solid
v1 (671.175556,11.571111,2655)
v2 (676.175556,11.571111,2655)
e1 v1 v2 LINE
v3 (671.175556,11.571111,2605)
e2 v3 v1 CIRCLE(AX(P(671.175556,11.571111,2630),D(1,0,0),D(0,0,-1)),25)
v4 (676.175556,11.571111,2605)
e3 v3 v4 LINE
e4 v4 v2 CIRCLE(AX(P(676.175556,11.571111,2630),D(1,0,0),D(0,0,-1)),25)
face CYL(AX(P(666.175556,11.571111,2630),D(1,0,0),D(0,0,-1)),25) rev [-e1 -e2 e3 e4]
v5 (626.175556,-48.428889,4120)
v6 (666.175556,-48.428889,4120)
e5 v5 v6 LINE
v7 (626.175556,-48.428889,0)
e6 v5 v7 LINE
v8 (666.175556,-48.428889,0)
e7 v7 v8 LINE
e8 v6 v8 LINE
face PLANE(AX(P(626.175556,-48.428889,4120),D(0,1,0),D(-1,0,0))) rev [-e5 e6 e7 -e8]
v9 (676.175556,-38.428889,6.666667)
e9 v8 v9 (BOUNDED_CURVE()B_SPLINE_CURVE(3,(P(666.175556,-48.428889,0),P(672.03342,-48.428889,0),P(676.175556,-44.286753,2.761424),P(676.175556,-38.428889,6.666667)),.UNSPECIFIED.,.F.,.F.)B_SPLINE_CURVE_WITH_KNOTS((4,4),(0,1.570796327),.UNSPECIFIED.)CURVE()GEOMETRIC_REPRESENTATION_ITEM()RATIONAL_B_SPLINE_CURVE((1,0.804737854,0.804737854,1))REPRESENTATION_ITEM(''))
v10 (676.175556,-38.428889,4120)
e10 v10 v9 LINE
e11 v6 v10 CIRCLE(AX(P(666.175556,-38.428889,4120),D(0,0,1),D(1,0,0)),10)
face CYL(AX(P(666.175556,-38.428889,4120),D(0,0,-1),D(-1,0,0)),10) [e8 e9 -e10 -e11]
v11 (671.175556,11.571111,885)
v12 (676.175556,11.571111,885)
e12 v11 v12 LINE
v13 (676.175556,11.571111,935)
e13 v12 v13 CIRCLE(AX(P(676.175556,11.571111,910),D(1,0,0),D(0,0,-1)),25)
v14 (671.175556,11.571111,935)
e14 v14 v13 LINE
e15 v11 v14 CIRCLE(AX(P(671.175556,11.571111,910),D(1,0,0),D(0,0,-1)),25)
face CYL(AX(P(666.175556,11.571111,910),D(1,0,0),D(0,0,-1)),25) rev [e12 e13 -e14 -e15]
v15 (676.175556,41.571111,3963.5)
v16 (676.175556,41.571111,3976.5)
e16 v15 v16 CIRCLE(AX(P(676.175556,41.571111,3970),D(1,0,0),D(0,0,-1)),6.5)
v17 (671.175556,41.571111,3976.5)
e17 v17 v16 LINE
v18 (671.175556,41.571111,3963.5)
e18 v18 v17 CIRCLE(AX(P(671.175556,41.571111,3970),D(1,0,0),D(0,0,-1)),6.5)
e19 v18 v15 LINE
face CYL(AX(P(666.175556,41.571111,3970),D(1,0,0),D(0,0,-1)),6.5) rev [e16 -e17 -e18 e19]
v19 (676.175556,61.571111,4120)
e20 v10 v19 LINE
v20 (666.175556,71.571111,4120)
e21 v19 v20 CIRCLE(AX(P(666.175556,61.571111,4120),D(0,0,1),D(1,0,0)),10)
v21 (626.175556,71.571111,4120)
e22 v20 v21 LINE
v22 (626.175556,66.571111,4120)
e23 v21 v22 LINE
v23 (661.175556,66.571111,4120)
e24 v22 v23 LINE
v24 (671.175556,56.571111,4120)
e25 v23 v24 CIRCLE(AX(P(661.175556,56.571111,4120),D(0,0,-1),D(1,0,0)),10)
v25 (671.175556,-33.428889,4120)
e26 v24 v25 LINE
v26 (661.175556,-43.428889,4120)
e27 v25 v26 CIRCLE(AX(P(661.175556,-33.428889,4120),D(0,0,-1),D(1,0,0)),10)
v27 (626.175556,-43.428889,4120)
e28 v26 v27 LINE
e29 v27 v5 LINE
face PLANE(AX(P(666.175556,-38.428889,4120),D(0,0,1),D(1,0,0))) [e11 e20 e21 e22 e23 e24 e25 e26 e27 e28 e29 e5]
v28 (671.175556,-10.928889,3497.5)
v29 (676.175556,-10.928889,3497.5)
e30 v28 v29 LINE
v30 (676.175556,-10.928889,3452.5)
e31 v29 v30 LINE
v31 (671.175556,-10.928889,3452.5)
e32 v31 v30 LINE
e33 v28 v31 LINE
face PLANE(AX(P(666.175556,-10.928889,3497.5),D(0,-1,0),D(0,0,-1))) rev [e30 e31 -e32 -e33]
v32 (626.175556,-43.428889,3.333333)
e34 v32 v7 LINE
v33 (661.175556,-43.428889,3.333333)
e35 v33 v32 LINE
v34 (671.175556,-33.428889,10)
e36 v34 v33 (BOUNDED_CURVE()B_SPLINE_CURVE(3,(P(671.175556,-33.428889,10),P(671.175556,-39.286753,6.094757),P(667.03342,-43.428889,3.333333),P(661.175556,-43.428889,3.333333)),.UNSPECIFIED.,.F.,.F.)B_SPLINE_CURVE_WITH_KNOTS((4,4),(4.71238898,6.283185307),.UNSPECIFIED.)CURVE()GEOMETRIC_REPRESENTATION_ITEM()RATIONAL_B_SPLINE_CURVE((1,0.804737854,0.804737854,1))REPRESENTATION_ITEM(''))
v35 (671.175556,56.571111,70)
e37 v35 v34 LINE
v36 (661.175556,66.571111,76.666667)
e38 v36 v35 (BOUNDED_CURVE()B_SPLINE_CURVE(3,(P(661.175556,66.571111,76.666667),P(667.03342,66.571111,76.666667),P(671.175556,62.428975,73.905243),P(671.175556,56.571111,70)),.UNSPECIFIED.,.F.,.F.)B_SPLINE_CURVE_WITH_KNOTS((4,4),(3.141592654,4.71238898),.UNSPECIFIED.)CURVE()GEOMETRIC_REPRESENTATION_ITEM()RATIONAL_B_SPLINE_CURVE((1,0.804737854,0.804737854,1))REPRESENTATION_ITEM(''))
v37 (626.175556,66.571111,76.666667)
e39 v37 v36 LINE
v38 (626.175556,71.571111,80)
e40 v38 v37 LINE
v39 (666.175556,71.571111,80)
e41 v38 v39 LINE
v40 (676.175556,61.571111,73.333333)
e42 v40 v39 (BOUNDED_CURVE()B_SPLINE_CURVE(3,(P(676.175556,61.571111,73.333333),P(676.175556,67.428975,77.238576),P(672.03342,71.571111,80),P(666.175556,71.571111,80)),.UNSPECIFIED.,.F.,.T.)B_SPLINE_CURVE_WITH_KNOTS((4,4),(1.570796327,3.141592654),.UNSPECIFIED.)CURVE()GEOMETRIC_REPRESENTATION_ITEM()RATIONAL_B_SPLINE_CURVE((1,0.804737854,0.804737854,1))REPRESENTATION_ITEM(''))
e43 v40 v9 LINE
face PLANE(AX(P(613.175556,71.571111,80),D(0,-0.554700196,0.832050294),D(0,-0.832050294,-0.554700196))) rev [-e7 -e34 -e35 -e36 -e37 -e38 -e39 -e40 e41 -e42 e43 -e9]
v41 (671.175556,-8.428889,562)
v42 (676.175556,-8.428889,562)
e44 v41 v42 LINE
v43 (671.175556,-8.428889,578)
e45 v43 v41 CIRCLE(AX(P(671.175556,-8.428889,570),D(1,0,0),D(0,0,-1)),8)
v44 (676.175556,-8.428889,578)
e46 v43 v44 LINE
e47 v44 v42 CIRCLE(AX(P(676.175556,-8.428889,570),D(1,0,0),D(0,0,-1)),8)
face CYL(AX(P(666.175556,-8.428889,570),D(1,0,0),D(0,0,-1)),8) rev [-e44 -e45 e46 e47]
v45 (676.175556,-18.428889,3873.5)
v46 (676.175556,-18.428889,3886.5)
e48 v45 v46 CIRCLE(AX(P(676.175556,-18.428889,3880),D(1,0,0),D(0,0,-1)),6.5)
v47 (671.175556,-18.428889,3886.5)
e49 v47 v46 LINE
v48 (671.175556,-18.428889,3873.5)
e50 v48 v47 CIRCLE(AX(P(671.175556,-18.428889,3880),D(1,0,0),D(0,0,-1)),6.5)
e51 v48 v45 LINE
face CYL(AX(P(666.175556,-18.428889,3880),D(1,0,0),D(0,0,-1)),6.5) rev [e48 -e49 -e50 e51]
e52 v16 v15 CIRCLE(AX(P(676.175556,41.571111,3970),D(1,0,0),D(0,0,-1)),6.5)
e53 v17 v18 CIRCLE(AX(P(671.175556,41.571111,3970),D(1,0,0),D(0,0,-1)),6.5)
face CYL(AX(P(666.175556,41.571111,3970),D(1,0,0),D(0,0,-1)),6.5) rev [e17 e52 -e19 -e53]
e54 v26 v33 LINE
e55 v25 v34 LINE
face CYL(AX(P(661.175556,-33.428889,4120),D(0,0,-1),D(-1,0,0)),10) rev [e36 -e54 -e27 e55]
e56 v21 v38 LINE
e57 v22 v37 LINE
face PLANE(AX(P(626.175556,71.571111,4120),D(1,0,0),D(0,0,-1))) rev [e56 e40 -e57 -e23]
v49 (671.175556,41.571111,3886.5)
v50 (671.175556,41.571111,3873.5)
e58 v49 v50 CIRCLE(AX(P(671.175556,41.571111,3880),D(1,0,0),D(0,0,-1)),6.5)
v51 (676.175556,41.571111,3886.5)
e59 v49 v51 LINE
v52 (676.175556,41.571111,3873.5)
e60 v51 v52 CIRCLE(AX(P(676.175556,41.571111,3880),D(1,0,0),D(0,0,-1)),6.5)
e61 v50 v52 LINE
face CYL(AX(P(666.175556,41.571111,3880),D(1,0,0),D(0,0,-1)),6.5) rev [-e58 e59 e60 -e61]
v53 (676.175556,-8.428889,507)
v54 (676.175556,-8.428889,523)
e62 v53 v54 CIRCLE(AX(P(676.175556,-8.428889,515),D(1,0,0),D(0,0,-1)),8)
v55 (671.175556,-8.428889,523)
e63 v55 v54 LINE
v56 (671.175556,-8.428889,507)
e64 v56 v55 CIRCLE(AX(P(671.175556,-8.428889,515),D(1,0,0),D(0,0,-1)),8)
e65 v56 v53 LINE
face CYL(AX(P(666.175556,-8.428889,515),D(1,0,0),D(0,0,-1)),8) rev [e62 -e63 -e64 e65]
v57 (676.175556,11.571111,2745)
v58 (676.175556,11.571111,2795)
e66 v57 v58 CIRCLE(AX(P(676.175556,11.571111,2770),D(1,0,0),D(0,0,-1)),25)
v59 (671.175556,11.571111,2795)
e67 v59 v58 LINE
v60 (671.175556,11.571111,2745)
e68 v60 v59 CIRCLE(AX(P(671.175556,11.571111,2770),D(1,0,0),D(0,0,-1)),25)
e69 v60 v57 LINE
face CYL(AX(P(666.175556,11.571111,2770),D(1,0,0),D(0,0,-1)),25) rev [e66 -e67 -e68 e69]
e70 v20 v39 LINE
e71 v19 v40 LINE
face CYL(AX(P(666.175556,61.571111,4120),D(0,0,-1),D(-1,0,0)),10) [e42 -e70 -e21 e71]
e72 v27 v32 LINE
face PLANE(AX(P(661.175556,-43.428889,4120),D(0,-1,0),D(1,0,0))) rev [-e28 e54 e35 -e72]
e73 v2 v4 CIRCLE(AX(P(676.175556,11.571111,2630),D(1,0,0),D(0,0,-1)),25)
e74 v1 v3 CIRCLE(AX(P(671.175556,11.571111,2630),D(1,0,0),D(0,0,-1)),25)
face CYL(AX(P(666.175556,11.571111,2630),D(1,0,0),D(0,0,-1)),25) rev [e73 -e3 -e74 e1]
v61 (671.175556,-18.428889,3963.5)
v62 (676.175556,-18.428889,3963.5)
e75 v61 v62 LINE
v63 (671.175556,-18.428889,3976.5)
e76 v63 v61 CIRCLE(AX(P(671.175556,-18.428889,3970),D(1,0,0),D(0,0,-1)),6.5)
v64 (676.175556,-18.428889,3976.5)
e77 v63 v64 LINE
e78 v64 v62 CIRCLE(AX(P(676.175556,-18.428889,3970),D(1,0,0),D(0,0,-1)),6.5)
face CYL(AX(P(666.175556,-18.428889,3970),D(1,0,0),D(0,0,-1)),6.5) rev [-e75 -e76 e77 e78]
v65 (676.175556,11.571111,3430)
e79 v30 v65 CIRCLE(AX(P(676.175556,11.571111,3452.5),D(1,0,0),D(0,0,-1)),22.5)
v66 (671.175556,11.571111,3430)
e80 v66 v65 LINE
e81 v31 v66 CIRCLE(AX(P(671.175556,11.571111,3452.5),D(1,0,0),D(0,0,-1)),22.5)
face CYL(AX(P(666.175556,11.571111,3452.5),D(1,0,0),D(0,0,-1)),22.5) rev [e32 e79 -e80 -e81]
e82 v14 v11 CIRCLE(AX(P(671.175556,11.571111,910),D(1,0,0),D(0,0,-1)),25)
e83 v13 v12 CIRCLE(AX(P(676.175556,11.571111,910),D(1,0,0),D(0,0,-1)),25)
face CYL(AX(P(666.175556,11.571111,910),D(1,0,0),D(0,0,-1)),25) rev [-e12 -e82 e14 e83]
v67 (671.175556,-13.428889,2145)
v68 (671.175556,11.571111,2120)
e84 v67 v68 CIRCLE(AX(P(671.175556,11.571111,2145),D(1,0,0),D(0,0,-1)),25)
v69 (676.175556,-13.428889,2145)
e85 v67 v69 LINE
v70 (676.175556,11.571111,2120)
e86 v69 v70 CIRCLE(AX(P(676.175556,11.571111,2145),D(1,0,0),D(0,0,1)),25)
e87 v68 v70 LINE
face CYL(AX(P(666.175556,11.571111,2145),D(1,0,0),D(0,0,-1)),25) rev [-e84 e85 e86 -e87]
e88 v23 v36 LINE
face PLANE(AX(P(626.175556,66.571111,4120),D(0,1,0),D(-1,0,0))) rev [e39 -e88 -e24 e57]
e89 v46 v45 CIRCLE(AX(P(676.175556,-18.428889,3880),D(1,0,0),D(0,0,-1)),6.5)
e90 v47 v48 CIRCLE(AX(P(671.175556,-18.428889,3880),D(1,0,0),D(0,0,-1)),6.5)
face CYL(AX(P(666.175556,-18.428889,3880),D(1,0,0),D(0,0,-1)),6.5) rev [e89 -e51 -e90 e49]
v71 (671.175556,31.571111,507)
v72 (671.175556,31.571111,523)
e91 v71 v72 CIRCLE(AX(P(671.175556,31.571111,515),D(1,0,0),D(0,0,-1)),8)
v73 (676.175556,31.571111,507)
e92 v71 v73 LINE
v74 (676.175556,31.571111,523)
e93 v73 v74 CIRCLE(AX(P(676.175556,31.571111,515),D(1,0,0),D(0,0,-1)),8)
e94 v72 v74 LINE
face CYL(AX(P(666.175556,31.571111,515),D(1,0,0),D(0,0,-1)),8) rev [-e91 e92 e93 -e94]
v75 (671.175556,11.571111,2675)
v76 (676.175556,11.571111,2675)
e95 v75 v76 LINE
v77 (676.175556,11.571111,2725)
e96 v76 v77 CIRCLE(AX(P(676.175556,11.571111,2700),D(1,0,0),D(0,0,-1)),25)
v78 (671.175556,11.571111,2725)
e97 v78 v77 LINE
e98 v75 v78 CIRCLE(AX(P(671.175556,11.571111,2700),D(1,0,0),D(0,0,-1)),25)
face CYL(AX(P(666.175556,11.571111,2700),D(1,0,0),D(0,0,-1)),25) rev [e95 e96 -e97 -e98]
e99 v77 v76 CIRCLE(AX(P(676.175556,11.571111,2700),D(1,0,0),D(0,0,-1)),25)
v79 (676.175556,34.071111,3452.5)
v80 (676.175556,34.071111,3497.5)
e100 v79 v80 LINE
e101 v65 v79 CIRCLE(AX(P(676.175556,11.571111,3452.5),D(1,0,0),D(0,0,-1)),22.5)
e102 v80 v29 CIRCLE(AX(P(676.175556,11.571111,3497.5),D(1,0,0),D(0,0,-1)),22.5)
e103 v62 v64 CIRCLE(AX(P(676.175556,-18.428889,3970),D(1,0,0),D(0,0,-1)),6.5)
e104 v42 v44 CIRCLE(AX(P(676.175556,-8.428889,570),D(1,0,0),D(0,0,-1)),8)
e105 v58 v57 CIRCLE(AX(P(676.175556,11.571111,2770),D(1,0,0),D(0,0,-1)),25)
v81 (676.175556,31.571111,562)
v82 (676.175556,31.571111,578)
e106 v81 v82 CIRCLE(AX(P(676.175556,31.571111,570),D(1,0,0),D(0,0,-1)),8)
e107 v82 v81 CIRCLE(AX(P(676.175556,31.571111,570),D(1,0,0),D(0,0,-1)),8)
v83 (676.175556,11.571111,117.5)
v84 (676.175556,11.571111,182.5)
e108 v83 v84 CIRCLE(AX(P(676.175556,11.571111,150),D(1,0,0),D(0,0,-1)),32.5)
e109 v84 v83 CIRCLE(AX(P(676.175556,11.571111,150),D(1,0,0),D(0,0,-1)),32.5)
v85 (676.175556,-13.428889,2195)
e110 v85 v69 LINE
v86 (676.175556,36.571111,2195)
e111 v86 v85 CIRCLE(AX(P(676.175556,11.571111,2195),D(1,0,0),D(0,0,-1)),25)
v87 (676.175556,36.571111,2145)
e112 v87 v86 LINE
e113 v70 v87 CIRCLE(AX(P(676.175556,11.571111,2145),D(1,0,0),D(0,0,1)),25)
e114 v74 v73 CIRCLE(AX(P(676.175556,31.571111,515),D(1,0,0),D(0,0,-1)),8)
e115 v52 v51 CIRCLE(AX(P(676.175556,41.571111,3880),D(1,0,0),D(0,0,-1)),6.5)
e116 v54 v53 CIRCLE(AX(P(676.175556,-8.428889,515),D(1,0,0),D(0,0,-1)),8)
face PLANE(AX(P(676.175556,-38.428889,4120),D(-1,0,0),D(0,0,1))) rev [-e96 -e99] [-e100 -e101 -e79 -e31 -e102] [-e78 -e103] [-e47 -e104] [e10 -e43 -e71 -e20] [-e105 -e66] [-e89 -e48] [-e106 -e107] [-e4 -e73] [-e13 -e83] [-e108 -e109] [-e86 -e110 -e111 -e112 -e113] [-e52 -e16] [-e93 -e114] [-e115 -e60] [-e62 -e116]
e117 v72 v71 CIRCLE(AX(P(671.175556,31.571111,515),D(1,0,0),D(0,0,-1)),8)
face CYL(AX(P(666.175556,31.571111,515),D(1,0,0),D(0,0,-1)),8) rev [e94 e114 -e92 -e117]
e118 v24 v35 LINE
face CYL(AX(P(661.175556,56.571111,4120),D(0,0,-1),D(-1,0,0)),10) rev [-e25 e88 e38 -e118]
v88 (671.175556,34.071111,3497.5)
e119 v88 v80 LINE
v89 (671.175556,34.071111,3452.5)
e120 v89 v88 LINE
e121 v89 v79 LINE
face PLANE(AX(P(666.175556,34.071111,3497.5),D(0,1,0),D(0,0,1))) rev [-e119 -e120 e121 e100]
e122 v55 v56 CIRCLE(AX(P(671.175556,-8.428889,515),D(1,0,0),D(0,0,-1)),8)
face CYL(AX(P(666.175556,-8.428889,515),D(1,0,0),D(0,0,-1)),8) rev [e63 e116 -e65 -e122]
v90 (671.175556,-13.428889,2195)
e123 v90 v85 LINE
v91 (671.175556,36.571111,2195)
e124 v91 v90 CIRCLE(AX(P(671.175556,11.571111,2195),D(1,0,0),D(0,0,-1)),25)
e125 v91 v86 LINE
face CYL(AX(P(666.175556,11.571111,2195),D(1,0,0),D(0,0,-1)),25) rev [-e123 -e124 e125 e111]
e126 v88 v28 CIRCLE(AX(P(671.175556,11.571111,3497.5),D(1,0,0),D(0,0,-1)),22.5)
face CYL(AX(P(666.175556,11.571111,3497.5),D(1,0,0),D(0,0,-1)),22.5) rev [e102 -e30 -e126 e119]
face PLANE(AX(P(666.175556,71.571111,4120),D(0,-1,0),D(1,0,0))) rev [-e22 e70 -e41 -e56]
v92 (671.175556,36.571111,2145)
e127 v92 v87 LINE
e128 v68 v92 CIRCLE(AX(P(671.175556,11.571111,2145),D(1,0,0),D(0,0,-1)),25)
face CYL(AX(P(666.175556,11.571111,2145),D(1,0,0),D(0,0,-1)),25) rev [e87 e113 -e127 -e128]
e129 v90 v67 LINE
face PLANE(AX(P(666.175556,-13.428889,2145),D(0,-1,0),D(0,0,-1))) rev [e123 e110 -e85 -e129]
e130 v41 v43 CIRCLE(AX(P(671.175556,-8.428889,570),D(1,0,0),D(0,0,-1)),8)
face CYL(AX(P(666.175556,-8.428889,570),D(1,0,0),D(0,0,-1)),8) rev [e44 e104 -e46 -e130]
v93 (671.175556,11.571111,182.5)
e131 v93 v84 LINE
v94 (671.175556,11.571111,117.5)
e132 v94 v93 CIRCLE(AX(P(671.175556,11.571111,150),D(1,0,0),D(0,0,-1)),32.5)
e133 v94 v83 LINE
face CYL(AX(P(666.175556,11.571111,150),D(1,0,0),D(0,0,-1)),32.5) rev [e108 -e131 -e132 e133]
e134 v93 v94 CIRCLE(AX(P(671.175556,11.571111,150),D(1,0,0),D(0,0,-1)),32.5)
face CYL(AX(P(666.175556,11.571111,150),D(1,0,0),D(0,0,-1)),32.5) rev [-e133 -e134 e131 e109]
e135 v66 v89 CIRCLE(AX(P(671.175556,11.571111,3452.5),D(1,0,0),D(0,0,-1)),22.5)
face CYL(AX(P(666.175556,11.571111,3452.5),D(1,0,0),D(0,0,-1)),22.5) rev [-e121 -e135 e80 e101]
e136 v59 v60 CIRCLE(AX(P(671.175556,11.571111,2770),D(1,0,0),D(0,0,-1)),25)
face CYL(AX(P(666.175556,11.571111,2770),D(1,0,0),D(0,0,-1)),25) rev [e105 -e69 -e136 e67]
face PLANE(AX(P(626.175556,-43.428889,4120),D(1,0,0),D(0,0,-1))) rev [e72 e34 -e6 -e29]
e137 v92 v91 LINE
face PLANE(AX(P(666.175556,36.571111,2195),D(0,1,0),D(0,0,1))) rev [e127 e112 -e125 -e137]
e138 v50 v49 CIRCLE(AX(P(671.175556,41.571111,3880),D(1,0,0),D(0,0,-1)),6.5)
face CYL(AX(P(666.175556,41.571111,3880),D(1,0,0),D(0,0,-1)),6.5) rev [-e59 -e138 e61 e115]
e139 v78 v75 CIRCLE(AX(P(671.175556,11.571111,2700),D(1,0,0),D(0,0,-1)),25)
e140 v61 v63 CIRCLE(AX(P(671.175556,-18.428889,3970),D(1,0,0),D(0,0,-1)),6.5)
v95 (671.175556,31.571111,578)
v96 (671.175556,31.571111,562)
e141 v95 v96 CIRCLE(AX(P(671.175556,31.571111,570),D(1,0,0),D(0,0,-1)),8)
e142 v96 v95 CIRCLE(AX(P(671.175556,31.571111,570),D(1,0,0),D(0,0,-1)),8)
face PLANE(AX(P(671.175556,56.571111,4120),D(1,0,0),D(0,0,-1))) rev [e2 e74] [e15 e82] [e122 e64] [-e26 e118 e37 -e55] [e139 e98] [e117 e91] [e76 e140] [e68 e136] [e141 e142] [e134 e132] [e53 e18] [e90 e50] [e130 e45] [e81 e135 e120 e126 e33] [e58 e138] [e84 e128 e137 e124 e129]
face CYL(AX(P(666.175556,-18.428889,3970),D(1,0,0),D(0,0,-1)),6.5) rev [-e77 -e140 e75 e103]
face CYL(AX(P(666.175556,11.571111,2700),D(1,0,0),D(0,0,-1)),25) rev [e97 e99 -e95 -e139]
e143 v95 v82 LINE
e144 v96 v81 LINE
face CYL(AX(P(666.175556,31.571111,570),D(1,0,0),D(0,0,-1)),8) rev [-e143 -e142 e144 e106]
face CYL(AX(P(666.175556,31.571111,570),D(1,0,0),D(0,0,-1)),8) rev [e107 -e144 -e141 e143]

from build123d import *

# Parameters (mm, degrees)
EXTRUDE_1_DEPTH     = 4120
SKETCH_2_R          = 6.5
SKETCH_2_R_2        = 25
SKETCH_2_R_3        = 22.5
SKETCH_2_R_4        = 8
CUT_EXTRUDE_2_DEPTH = 10
CUT_EXTRUDE_3_DEPTH = 10
SKETCH_4_R          = 6.5
CUT_EXTRUDE_4_DEPTH = 10
SKETCH_5_W          = 22.746399217
SKETCH_5_H          = 81.53462818
SKETCH_5_R          = 6.5
EXTRUDE_2_DEPTH     = 5
SKETCH_6_R          = 32.5
CUT_EXTRUDE_5_DEPTH = 10
CUT_EXTRUDE_6_DEPTH = 63


with BuildPart() as part:
    # 草图1 → 凸台-拉伸1 (new body)
    with BuildSketch(Plane.XY):
        with BuildLine():
            Line((626.175555556, -48.428888889), (666.175555556, -48.428888889))
            ThreePointArc((666.175555556, -48.428888889), (673.246623367, -45.499956701), (676.175555556, -38.428888889))
            Line((676.175555556, -38.428888889), (676.175555556, 61.571111111))
            ThreePointArc((676.175555556, 61.571111111), (673.246623367, 68.642178923), (666.175555556, 71.571111111))
            Line((666.175555556, 71.571111111), (626.175555556, 71.571111111))
            Line((626.175555556, 71.571111111), (626.175555556, 66.571111111))
            Line((626.175555556, 66.571111111), (661.175555556, 66.571111111))
            ThreePointArc((661.175555556, 66.571111111), (668.246623367, 63.642178923), (671.175555556, 56.571111111))
            Line((671.175555556, 56.571111111), (671.175555556, -33.428888889))
            ThreePointArc((671.175555556, -33.428888889), (668.246623367, -40.499956701), (661.175555556, -43.428888889))
            Line((661.175555556, -43.428888889), (626.175555556, -43.428888889))
            Line((626.175555556, -43.428888889), (626.175555556, -48.428888889))
        make_face()
    extrude(amount=EXTRUDE_1_DEPTH)

    # 草图2 → 切除-拉伸2 (cut)
    with BuildSketch(Plane(origin=(676.175555556, 0, 0), x_dir=(0, 0, -1), z_dir=(1, 0, 0))):
        with Locations((-3985, -18.428888889)):
            Circle(SKETCH_2_R)
        with Locations((-3985, 41.571111111)):
            Circle(SKETCH_2_R)
        with Locations((-3895, 41.571111111)):
            Circle(SKETCH_2_R)
        with Locations((-3895, -18.428888889)):
            Circle(SKETCH_2_R)
        with Locations((-2770, 11.571111111)):
            Circle(SKETCH_2_R_2)
        with Locations((-2700, 11.571111111)):
            Circle(SKETCH_2_R_2)
        with Locations((-2630, 11.571111111)):
            Circle(SKETCH_2_R_2)
        with Locations((-150, 11.571111111)):
            Circle(SKETCH_2_R_3)
        with Locations((-570, 31.571111111)):
            Circle(SKETCH_2_R_4)
        with Locations((-515, 31.571111111)):
            Circle(SKETCH_2_R_4)
        with Locations((-570, -8.428888889)):
            Circle(SKETCH_2_R_4)
        with Locations((-515, -8.428888889)):
            Circle(SKETCH_2_R_4)
        with BuildLine():
            Line((-3497.5, 34.071111111), (-3452.5, 34.071111111))
            ThreePointArc((-3452.5, 34.071111111), (-3430, 11.571111111), (-3452.5, -10.928888889))
            Line((-3452.5, -10.928888889), (-3497.5, -10.928888889))
            ThreePointArc((-3497.5, -10.928888889), (-3520, 11.571111111), (-3497.5, 34.071111111))
        make_face()
        with BuildLine():
            Line((-2195, 36.571111111), (-2145, 36.571111111))
            ThreePointArc((-2145, 36.571111111), (-2120, 11.571111111), (-2145, -13.428888889))
            Line((-2145, -13.428888889), (-2195, -13.428888889))
            ThreePointArc((-2195, -13.428888889), (-2220, 11.571111111), (-2195, 36.571111111))
        make_face()
    extrude(amount=-CUT_EXTRUDE_2_DEPTH, mode=Mode.SUBTRACT)

    # 草图3 → 切除-拉伸3 (cut)
    with BuildSketch(Plane(origin=(676.175555556, 0, 0), x_dir=(0, 0, -1), z_dir=(1, 0, 0))):
        with BuildLine():
            ThreePointArc((-885, 11.571111111), (-892.32233047, 29.248780641), (-910, 36.571111111))
            Line((-910, 36.571111111), (-910, -13.428888889))
            ThreePointArc((-910, -13.428888889), (-892.32233047, -6.106558419), (-885, 11.571111111))
        make_face()
        with BuildLine():
            Line((-910, -13.428888889), (-910, 36.571111111))
            ThreePointArc((-910, 36.571111111), (-935, 11.571111111), (-910, -13.428888889))
        make_face()
    extrude(amount=-CUT_EXTRUDE_3_DEPTH, mode=Mode.SUBTRACT)

    # 草图4 → 切除-拉伸4 (cut)
    with BuildSketch(Plane(origin=(676.175555556, 0, 0), x_dir=(0, 0, -1), z_dir=(1, 0, 0))):
        with Locations((-3880, 41.571111111)):
            Circle(SKETCH_4_R)
        with Locations((-3970, 41.571111111)):
            Circle(SKETCH_4_R)
        with Locations((-3970, -18.428888889)):
            Circle(SKETCH_4_R)
        with Locations((-3880, -18.428888889)):
            Circle(SKETCH_4_R)
    extrude(amount=-CUT_EXTRUDE_4_DEPTH, mode=Mode.SUBTRACT)

    # 草图5 → 凸台-拉伸2 (add)
    # profile 1 of 6: a face of its own
    with BuildSketch(Plane(origin=(676.175555556, 0, 0), x_dir=(0, 0, -1), z_dir=(1, 0, 0))):
        with Locations((-3988.902277588, 11.372267682)):
            Rectangle(SKETCH_5_W, SKETCH_5_H)
        with Locations((-3985, 41.571111111)):
            Circle(SKETCH_5_R, mode=Mode.SUBTRACT)
        with Locations((-3985, -18.428888889)):
            Circle(SKETCH_5_R, mode=Mode.SUBTRACT)
    # profile 2 of 6: a face of its own
    with BuildSketch(Plane(origin=(676.175555556, 0, 0), x_dir=(0, 0, -1), z_dir=(1, 0, 0))):
        Polygon((-3887.411741686, 56.036728607), (-3911.283955206, 53.905280971), (-3903.726029575, -30.743486096), (-3887.411741686, -30.743486096), (-3887.411741686, -18.428888889), align=None)
        with Locations((-3895, -18.428888889)):
            Circle(SKETCH_5_R, mode=Mode.SUBTRACT)
        with Locations((-3895, 41.571111111)):
            Circle(SKETCH_5_R, mode=Mode.SUBTRACT)
    # profile 3 of 6: a face of its own
    with BuildSketch(Plane(origin=(676.175555556, 0, 0), x_dir=(0, 0, -1), z_dir=(1, 0, 0))):
        with Locations((-3985, 41.571111111)):
            Circle(SKETCH_5_R)
    # profile 4 of 6: a face of its own
    with BuildSketch(Plane(origin=(676.175555556, 0, 0), x_dir=(0, 0, -1), z_dir=(1, 0, 0))):
        with Locations((-3985, -18.428888889)):
            Circle(SKETCH_5_R)
    # profile 5 of 6: a face of its own
    with BuildSketch(Plane(origin=(676.175555556, 0, 0), x_dir=(0, 0, -1), z_dir=(1, 0, 0))):
        with Locations((-3895, -18.428888889)):
            Circle(SKETCH_5_R)
    # profile 6 of 6: a face of its own
    with BuildSketch(Plane(origin=(676.175555556, 0, 0), x_dir=(0, 0, -1), z_dir=(1, 0, 0))):
        with Locations((-3895, 41.571111111)):
            Circle(SKETCH_5_R)
    extrude(amount=-EXTRUDE_2_DEPTH)

    # 草图6 → 切除-拉伸5 (cut)
    with BuildSketch(Plane(origin=(676.175555556, 0, 0), x_dir=(0, 0, -1), z_dir=(1, 0, 0))):
        with Locations((-150, 11.571111111)):
            Circle(SKETCH_6_R)
    extrude(amount=-CUT_EXTRUDE_5_DEPTH, mode=Mode.SUBTRACT)

    # 草图7 → 切除-拉伸6 (cut)
    with BuildSketch(Plane(origin=(676.175555556, 0, 0), x_dir=(0, 0, -1), z_dir=(1, 0, 0))):
        Polygon((0, 71.571111111), (-80, 71.571111111), (0, -48.428888889), align=None)
    extrude(amount=-CUT_EXTRUDE_6_DEPTH, mode=Mode.SUBTRACT)


solid = part.part
